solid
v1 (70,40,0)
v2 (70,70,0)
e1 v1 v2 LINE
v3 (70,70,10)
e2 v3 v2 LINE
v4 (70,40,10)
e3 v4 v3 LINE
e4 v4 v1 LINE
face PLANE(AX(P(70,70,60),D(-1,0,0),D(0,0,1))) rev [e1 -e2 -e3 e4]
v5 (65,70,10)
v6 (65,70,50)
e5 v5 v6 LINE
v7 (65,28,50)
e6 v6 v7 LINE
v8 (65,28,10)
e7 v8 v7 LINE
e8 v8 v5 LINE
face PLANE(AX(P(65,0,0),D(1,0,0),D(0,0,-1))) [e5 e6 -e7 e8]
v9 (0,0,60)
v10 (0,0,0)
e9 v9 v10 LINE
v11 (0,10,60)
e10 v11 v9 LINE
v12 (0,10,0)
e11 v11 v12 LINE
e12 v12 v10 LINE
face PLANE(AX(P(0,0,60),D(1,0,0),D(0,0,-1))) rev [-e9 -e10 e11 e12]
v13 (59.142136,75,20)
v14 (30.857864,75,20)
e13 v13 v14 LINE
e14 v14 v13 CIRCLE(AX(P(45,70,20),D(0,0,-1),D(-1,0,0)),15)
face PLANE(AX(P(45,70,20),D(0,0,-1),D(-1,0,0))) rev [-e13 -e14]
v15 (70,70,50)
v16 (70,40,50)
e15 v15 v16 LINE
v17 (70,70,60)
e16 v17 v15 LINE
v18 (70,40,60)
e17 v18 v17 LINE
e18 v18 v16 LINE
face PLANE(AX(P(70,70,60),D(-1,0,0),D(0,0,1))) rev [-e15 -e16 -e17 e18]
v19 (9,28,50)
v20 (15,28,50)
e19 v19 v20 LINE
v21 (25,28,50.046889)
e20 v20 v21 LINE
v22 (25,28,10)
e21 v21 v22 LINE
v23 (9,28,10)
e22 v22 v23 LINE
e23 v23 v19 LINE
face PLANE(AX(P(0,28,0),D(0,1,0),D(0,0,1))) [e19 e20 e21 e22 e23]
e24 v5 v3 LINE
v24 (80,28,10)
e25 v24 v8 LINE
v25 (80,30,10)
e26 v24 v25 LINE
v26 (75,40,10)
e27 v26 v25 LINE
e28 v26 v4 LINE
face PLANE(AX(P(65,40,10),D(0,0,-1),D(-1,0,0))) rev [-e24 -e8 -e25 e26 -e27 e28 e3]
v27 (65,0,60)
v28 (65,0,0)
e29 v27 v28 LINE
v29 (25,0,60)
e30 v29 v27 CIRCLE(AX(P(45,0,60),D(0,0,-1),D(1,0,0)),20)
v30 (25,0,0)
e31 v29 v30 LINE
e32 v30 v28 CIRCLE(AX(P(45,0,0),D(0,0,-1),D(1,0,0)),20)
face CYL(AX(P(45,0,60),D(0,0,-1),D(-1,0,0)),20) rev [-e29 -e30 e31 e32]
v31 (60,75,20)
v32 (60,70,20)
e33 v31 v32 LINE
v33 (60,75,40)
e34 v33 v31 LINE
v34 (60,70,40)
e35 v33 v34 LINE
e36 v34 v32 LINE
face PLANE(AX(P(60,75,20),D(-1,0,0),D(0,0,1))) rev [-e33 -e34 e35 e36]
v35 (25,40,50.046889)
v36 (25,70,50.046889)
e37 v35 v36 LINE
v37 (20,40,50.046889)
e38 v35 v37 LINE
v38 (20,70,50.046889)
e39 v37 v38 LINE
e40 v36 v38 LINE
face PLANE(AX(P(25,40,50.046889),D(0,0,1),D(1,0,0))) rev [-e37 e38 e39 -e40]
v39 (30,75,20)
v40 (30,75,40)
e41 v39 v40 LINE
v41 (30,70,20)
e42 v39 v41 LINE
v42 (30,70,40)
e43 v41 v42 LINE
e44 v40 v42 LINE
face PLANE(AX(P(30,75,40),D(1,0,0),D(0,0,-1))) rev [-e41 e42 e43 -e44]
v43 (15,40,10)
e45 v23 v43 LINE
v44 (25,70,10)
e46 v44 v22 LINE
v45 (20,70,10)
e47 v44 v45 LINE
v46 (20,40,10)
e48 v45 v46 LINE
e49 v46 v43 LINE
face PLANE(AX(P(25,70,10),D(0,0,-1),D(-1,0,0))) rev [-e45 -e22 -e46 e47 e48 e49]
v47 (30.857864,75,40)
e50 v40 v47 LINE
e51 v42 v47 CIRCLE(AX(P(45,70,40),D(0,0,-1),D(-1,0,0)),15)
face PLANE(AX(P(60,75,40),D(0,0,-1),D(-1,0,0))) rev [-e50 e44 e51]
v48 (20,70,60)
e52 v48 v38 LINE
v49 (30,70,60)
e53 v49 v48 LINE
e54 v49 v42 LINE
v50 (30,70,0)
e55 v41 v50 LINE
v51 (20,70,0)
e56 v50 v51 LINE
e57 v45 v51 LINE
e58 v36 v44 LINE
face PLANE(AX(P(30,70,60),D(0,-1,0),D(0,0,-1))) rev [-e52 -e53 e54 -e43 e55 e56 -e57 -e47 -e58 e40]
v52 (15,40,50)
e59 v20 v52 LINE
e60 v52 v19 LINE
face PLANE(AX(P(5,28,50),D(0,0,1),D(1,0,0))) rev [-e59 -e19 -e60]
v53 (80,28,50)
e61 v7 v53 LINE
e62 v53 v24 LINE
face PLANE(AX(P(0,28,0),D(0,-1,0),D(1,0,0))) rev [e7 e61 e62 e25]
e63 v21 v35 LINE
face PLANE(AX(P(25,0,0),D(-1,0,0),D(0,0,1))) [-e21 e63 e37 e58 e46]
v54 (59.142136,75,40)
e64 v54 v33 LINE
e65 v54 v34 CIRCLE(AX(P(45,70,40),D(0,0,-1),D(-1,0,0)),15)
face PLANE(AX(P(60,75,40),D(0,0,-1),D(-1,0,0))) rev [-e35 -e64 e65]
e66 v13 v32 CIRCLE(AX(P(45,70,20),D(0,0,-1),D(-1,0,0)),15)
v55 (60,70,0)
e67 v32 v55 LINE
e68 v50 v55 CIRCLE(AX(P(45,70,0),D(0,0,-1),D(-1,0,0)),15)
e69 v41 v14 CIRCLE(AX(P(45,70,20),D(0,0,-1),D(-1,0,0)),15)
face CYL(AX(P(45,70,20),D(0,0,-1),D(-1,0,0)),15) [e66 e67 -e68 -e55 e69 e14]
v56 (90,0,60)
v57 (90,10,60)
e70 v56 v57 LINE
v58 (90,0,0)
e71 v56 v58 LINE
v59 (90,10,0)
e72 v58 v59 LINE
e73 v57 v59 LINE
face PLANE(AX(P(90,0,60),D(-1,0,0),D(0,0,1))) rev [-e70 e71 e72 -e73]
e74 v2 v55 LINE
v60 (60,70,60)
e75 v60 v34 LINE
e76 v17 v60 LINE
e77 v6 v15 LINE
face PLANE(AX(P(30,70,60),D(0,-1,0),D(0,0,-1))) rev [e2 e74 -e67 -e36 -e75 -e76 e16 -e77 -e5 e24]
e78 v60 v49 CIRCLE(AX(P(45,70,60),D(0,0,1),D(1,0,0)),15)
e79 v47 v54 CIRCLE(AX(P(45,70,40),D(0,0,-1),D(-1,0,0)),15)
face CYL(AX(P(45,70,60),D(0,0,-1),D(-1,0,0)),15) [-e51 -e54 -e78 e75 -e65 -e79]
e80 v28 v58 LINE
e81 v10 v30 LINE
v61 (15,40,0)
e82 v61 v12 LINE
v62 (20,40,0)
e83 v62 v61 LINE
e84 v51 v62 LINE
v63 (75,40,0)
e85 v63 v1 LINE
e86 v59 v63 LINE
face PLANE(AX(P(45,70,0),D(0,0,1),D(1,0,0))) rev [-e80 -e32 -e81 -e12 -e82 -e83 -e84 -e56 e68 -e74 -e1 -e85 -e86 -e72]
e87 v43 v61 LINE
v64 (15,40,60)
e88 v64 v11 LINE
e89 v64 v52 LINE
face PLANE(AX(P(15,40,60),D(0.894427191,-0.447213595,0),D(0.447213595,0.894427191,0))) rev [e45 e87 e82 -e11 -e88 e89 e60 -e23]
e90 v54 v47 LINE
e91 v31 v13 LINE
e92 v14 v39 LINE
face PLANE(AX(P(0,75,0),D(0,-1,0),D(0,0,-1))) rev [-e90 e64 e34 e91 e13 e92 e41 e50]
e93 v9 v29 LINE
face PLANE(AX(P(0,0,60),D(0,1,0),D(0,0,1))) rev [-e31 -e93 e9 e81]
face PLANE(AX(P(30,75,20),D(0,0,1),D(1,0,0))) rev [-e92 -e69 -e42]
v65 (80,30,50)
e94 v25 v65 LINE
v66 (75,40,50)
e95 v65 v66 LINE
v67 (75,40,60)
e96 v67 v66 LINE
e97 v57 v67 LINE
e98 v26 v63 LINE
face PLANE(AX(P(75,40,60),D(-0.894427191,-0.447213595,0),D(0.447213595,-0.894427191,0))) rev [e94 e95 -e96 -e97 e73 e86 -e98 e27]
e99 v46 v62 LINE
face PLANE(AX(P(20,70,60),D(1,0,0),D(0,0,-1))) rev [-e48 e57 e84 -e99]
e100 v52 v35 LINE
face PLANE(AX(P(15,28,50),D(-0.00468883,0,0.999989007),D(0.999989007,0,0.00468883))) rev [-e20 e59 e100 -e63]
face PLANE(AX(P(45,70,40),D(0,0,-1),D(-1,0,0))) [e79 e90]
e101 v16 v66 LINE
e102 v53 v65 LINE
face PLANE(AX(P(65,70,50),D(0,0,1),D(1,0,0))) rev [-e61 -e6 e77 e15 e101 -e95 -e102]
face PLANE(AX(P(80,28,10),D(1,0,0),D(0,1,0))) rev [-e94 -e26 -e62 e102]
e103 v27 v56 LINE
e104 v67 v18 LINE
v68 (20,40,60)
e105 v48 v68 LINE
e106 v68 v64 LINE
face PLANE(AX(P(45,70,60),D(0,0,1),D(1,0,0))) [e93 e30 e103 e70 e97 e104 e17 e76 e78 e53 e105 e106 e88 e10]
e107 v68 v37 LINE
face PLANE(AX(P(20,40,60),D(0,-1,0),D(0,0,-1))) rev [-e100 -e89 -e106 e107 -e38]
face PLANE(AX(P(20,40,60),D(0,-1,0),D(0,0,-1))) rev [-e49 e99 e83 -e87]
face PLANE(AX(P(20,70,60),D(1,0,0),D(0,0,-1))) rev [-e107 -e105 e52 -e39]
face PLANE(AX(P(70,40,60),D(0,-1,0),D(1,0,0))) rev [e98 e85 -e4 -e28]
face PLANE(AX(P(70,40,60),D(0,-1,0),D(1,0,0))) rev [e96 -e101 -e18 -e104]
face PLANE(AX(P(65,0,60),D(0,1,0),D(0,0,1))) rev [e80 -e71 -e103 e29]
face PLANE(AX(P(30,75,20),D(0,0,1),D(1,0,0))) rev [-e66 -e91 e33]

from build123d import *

# Parameters (mm, degrees)
ARCHED_BODY_60_DEPTH         = 60
POCKET_A_STEP_CUT_5_DEPTH    = 5
POCKET_A_CUT_12_DEPTH        = 12
POCKET_B_STEP_CUT_5_DEPTH    = 5
POCKET_B_SKETCH_W            = 15
POCKET_B_SKETCH_H            = 40
POCKET_B_CUT_12_DEPTH        = 12
TOP_HALF_ROUND_CUT_40_DEPTH  = 40
TOP_PAD_SKETCH_W             = 30
TOP_PAD_SKETCH_H             = 20
TOP_PAD_5_DEPTH              = 5
TOP_HALF_ROUND_BOSS_20_DEPTH = 20


with BuildPart() as part:
    # Arched Body Profile Sketch → Arched Body 60 (new body)
    with BuildSketch(Plane.XY):
        with BuildLine():
            Line((0, 0), (25, 0))
            ThreePointArc((25, 0), (45, 20), (65, 0))
            Line((65, 0), (90, 0))
            Line((90, 0), (90, 10))
            Line((90, 10), (75, 40))
            Line((75, 40), (70, 40))
            Line((70, 40), (70, 70))
            Line((70, 70), (60, 70))
            ThreePointArc((60, 70), (45, 85), (30, 70))
            Line((30, 70), (20, 70))
            Line((20, 70), (20, 40))
            Line((20, 40), (15, 40))
            Line((15, 40), (0, 10))
            Line((0, 10), (0, 0))
        make_face()
    extrude(amount=ARCHED_BODY_60_DEPTH)

    # Pocket A Step Sketch → Pocket A Step Cut 5 (cut)
    with BuildSketch(Plane.ZY.offset(-20)):
        Polygon((30, 70), (10, 70), (10, 40), (50.046888812, 40), (50.046888812, 70), align=None)
    extrude(amount=-POCKET_A_STEP_CUT_5_DEPTH, mode=Mode.SUBTRACT)

    # Pocket A Sketch → Pocket A Cut 12 (cut)
    with BuildSketch(Plane(origin=(0, 40, 0), x_dir=(1, 0, 0), z_dir=(0, 1, 0))):
        Polygon((20, -10), (15, -10), (5, -10), (5, -50), (15, -50), (25, -50.046888812), (25, -10), align=None)
    extrude(amount=-POCKET_A_CUT_12_DEPTH, mode=Mode.SUBTRACT)

    # Pocket B Step Sketch → Pocket B Step Cut 5 (cut)
    with BuildSketch(Plane(origin=(70, 0, 0), x_dir=(0, 0, -1), z_dir=(1, 0, 0))):
        Polygon((-30, 70), (-50, 70), (-50, 40), (-10, 40), (-10, 70), align=None)
    extrude(amount=-POCKET_B_STEP_CUT_5_DEPTH, mode=Mode.SUBTRACT)

    # Pocket B Sketch → Pocket B Cut 12 (cut)
    with BuildSketch(Plane(origin=(0, 40, 0), x_dir=(1, 0, 0), z_dir=(0, 1, 0))):
        with Locations((72.5, -30)):
            Rectangle(POCKET_B_SKETCH_W, POCKET_B_SKETCH_H)
    extrude(amount=-POCKET_B_CUT_12_DEPTH, mode=Mode.SUBTRACT)

    # Top Half-Round Cut Sketch → Top Half-Round Cut 40 (cut)
    with BuildSketch(Plane(origin=(0, 0, 0), x_dir=(-1, 0, 0), z_dir=(0, 0, -1))):
        with BuildLine():
            Line((-60, 70), (-30, 70))
            ThreePointArc((-30, 70), (-45, 85), (-60, 70))
        make_face()
    extrude(amount=-TOP_HALF_ROUND_CUT_40_DEPTH, mode=Mode.SUBTRACT)

    # Top Pad Sketch → Top Pad 5 (add)
    with BuildSketch(Plane(origin=(0, 70, 0), x_dir=(1, 0, 0), z_dir=(0, 1, 0))):
        with Locations((45, -30)):
            Rectangle(TOP_PAD_SKETCH_W, TOP_PAD_SKETCH_H)
    extrude(amount=TOP_PAD_5_DEPTH)

    # Top Half-Round Boss Sketch → Top Half-Round Boss 20 (add)
    with BuildSketch(Plane(origin=(0, 0, 0), x_dir=(-1, 0, 0), z_dir=(0, 0, -1))):
        with BuildLine():
            Line((-60, 70), (-30, 70))
            ThreePointArc((-30, 70), (-45, 85), (-60, 70))
        make_face()
    extrude(amount=-TOP_HALF_ROUND_BOSS_20_DEPTH)


solid = part.part
